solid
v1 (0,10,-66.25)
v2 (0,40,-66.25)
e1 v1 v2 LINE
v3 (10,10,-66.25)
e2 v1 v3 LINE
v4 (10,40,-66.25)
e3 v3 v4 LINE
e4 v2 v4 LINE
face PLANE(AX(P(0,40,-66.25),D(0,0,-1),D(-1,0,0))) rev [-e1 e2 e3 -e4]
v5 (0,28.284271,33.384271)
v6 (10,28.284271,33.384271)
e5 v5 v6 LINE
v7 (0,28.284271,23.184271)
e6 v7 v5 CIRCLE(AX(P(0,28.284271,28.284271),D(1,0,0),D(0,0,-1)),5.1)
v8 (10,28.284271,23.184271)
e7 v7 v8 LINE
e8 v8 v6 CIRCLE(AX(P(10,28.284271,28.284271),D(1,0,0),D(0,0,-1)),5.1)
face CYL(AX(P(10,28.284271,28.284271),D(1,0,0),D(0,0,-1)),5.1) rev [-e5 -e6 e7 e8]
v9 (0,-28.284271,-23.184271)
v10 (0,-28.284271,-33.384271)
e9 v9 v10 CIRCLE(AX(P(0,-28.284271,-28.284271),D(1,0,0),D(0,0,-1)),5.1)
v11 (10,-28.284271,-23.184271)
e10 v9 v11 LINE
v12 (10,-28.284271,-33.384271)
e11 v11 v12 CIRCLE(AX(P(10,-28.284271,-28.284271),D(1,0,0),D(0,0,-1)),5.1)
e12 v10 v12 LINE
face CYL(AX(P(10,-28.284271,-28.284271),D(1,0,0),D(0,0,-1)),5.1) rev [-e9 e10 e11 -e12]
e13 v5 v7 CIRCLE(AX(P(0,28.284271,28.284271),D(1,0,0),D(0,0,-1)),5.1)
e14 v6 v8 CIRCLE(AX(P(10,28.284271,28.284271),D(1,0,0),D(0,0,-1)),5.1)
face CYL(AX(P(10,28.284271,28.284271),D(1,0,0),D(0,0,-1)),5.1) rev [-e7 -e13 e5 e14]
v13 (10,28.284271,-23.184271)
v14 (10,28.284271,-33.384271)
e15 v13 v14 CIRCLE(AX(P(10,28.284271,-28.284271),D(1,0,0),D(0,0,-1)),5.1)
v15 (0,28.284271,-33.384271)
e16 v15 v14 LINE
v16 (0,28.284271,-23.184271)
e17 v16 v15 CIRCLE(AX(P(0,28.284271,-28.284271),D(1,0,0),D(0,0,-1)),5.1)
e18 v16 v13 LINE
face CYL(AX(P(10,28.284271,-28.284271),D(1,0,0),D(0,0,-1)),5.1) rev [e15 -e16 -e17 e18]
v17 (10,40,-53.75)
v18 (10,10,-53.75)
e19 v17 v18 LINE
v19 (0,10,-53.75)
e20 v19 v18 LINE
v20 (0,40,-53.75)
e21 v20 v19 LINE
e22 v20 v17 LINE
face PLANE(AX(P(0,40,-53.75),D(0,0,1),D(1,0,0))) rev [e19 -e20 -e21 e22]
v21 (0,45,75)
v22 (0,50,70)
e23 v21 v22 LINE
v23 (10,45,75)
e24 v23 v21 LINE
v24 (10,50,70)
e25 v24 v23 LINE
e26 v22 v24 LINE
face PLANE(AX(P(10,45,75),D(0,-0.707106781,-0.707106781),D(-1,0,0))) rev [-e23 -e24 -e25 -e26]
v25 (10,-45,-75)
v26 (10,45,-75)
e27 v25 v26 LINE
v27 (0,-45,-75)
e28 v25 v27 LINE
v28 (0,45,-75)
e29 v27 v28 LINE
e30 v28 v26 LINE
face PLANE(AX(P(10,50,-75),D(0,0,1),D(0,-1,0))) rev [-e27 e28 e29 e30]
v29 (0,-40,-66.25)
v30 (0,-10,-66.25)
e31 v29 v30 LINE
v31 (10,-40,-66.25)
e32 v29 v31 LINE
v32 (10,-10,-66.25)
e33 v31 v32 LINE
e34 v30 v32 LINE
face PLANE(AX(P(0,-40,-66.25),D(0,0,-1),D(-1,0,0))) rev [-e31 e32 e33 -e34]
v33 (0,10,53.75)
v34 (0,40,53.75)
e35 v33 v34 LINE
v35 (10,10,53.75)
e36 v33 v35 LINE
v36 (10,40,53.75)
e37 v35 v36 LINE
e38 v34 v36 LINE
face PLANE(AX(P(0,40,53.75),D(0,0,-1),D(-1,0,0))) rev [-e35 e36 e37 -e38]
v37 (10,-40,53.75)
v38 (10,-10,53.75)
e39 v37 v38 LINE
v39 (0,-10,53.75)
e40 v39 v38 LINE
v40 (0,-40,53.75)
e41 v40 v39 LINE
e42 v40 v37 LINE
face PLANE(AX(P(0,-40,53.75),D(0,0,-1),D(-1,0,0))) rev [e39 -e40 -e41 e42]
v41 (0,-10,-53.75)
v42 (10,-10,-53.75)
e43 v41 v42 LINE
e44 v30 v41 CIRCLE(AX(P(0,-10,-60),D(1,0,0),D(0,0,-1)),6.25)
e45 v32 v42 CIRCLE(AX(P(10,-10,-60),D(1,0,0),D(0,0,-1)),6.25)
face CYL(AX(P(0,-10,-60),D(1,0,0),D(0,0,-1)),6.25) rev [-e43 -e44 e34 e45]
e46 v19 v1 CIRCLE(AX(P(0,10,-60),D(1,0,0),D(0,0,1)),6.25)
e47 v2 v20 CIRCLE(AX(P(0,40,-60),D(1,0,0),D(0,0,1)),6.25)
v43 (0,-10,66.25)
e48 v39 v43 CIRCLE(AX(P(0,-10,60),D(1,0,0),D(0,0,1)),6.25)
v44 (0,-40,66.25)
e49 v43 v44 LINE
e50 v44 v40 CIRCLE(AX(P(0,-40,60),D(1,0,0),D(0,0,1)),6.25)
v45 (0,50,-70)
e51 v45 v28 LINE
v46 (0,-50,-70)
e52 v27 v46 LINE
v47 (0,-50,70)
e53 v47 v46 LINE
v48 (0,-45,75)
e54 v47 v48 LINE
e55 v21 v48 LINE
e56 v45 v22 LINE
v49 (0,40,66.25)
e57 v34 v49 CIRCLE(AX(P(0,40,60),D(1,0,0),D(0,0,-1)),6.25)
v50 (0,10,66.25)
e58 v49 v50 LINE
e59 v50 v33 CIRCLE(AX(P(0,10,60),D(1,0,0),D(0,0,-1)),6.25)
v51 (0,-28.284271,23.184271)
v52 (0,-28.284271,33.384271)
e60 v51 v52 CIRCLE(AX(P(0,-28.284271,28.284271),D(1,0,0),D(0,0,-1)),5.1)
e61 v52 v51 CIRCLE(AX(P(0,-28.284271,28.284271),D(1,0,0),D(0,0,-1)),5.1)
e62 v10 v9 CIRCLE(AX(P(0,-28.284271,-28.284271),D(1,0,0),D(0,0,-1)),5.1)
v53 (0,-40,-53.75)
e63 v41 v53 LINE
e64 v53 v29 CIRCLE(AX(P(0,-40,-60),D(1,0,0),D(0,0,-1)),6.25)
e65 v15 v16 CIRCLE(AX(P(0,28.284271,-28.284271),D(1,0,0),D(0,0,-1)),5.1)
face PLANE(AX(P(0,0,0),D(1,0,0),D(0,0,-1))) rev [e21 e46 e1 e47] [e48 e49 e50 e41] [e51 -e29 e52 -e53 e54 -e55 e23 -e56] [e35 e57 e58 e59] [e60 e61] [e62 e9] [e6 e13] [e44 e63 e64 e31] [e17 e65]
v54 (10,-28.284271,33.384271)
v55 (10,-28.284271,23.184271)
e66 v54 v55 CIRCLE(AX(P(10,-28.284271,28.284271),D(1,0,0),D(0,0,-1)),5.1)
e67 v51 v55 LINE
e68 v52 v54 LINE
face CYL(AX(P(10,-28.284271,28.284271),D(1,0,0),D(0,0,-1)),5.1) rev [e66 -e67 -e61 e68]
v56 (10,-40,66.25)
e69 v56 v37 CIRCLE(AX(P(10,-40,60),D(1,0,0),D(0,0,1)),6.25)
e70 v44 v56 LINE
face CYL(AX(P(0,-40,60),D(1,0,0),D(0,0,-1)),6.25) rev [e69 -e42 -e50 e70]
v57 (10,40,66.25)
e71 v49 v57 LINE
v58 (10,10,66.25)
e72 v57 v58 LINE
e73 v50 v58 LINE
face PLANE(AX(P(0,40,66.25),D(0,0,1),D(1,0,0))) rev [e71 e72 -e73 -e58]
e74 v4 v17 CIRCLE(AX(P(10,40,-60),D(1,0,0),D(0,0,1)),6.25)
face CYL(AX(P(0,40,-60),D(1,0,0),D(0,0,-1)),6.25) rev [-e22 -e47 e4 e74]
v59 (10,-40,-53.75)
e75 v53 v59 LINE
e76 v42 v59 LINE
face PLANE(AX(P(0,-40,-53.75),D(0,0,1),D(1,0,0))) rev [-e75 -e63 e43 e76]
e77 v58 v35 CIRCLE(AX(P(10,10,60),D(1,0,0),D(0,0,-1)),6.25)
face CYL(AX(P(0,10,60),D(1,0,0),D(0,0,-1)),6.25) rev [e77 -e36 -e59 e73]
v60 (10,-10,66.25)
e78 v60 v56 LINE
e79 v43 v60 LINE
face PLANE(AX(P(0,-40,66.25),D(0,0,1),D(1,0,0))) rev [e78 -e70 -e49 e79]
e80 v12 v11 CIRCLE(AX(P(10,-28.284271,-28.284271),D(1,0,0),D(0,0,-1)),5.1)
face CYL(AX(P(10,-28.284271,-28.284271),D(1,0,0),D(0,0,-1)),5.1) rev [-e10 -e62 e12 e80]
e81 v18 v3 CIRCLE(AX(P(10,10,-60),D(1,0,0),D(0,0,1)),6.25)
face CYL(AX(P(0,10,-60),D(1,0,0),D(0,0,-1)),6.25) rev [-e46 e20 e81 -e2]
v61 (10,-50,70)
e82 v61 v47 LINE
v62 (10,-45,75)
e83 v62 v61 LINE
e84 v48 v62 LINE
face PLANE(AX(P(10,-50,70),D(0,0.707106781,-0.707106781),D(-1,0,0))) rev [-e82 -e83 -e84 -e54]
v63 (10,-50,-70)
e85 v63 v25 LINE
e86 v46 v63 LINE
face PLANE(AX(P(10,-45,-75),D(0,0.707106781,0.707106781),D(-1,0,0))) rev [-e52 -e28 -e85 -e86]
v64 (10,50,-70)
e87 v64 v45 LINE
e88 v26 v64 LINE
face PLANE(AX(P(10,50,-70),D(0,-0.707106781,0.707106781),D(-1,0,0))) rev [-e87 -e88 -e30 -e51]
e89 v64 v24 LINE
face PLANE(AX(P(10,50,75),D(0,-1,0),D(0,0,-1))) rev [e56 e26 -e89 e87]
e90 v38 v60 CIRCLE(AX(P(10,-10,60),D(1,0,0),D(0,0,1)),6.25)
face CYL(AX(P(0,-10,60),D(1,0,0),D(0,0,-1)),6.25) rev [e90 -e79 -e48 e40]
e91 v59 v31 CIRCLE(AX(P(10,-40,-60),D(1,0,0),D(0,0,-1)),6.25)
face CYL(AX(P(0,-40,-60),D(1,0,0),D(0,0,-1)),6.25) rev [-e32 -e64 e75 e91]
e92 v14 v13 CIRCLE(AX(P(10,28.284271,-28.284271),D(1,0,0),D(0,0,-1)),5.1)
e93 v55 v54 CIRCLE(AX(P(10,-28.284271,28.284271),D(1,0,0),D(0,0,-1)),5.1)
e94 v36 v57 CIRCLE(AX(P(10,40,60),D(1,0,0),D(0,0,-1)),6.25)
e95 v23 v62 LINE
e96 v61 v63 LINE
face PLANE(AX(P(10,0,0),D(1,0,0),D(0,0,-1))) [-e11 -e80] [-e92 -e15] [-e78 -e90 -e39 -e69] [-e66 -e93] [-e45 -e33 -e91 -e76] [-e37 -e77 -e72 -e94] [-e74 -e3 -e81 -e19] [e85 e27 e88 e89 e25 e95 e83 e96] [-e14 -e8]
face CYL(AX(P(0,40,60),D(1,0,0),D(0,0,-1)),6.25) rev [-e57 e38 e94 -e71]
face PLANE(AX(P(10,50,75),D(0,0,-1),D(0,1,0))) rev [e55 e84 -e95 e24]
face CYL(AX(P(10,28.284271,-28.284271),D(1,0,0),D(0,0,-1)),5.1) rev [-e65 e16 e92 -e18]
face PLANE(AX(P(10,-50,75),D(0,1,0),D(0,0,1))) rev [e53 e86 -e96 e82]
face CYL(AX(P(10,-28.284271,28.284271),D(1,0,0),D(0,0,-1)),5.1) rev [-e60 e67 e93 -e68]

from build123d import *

# Parameters (mm, degrees)
SKETCH_1_W          = 150
SKETCH_1_H          = 100
EXTRUDE_1_DEPTH     = 10
HOLE_WIZARD_M12_1_D = 10.2
CUT_EXTRUDE_1_DEPTH = 91.691785736
CHAMFER_1_SIZE      = 5


with BuildPart() as part:
    # 草图1 → 凸台-拉伸1 (new body)
    with BuildSketch(Plane(origin=(0, 0, 0), x_dir=(0, 0, -1), z_dir=(1, 0, 0))):
        Rectangle(SKETCH_1_W, SKETCH_1_H)
    extrude(amount=EXTRUDE_1_DEPTH)

    # M12 螺纹孔1 (through all)
    with Locations(Plane(origin=(10, 0, 0), x_dir=(0, 0, -1), z_dir=(1, 0, 0))):
        with Locations((-28.284271247, 28.284271247), (28.284271247, 28.284271247), (28.284271247, -28.284271247), (-28.284271247, -28.284271247)):
            Hole(HOLE_WIZARD_M12_1_D / 2)

    # 草图4 → 切除-拉伸1 (cut, through all)
    with BuildSketch(Plane(origin=(10, 0, 0), x_dir=(0, 0, -1), z_dir=(1, 0, 0))):
        with BuildLine():
            Line((-53.75, 40), (-53.75, 10))
            ThreePointArc((-53.75, 10), (-60, 3.75), (-66.25, 10))
            Line((-66.25, 10), (-66.25, 40))
            ThreePointArc((-66.25, 40), (-60, 46.25), (-53.75, 40))
        make_face()
        with BuildLine():
            Line((53.75, 40), (53.75, 10))
            ThreePointArc((53.75, 10), (60, 3.75), (66.25, 10))
            Line((66.25, 10), (66.25, 40))
            ThreePointArc((66.25, 40), (60, 46.25), (53.75, 40))
        make_face()
        with BuildLine():
            Line((-53.75, -40), (-53.75, -10))
            ThreePointArc((-53.75, -10), (-60, -3.75), (-66.25, -10))
            Line((-66.25, -10), (-66.25, -40))
            ThreePointArc((-66.25, -40), (-60, -46.25), (-53.75, -40))
        make_face()
        with BuildLine():
            Line((53.75, -40), (53.75, -10))
            ThreePointArc((53.75, -10), (60, -3.75), (66.25, -10))
            Line((66.25, -10), (66.25, -40))
            ThreePointArc((66.25, -40), (60, -46.25), (53.75, -40))
        make_face()
    extrude(amount=-CUT_EXTRUDE_1_DEPTH, mode=Mode.SUBTRACT)

    # 倒角1
    chamfer_1_edges = [part.edges().sort_by_distance(p)[0] for p in [
        (5, -50, -75),
        (5, -50, 75),
        (5, 50, 75),
        (5, 50, -75),
    ]]
    chamfer(chamfer_1_edges, length=CHAMFER_1_SIZE)


solid = part.part
